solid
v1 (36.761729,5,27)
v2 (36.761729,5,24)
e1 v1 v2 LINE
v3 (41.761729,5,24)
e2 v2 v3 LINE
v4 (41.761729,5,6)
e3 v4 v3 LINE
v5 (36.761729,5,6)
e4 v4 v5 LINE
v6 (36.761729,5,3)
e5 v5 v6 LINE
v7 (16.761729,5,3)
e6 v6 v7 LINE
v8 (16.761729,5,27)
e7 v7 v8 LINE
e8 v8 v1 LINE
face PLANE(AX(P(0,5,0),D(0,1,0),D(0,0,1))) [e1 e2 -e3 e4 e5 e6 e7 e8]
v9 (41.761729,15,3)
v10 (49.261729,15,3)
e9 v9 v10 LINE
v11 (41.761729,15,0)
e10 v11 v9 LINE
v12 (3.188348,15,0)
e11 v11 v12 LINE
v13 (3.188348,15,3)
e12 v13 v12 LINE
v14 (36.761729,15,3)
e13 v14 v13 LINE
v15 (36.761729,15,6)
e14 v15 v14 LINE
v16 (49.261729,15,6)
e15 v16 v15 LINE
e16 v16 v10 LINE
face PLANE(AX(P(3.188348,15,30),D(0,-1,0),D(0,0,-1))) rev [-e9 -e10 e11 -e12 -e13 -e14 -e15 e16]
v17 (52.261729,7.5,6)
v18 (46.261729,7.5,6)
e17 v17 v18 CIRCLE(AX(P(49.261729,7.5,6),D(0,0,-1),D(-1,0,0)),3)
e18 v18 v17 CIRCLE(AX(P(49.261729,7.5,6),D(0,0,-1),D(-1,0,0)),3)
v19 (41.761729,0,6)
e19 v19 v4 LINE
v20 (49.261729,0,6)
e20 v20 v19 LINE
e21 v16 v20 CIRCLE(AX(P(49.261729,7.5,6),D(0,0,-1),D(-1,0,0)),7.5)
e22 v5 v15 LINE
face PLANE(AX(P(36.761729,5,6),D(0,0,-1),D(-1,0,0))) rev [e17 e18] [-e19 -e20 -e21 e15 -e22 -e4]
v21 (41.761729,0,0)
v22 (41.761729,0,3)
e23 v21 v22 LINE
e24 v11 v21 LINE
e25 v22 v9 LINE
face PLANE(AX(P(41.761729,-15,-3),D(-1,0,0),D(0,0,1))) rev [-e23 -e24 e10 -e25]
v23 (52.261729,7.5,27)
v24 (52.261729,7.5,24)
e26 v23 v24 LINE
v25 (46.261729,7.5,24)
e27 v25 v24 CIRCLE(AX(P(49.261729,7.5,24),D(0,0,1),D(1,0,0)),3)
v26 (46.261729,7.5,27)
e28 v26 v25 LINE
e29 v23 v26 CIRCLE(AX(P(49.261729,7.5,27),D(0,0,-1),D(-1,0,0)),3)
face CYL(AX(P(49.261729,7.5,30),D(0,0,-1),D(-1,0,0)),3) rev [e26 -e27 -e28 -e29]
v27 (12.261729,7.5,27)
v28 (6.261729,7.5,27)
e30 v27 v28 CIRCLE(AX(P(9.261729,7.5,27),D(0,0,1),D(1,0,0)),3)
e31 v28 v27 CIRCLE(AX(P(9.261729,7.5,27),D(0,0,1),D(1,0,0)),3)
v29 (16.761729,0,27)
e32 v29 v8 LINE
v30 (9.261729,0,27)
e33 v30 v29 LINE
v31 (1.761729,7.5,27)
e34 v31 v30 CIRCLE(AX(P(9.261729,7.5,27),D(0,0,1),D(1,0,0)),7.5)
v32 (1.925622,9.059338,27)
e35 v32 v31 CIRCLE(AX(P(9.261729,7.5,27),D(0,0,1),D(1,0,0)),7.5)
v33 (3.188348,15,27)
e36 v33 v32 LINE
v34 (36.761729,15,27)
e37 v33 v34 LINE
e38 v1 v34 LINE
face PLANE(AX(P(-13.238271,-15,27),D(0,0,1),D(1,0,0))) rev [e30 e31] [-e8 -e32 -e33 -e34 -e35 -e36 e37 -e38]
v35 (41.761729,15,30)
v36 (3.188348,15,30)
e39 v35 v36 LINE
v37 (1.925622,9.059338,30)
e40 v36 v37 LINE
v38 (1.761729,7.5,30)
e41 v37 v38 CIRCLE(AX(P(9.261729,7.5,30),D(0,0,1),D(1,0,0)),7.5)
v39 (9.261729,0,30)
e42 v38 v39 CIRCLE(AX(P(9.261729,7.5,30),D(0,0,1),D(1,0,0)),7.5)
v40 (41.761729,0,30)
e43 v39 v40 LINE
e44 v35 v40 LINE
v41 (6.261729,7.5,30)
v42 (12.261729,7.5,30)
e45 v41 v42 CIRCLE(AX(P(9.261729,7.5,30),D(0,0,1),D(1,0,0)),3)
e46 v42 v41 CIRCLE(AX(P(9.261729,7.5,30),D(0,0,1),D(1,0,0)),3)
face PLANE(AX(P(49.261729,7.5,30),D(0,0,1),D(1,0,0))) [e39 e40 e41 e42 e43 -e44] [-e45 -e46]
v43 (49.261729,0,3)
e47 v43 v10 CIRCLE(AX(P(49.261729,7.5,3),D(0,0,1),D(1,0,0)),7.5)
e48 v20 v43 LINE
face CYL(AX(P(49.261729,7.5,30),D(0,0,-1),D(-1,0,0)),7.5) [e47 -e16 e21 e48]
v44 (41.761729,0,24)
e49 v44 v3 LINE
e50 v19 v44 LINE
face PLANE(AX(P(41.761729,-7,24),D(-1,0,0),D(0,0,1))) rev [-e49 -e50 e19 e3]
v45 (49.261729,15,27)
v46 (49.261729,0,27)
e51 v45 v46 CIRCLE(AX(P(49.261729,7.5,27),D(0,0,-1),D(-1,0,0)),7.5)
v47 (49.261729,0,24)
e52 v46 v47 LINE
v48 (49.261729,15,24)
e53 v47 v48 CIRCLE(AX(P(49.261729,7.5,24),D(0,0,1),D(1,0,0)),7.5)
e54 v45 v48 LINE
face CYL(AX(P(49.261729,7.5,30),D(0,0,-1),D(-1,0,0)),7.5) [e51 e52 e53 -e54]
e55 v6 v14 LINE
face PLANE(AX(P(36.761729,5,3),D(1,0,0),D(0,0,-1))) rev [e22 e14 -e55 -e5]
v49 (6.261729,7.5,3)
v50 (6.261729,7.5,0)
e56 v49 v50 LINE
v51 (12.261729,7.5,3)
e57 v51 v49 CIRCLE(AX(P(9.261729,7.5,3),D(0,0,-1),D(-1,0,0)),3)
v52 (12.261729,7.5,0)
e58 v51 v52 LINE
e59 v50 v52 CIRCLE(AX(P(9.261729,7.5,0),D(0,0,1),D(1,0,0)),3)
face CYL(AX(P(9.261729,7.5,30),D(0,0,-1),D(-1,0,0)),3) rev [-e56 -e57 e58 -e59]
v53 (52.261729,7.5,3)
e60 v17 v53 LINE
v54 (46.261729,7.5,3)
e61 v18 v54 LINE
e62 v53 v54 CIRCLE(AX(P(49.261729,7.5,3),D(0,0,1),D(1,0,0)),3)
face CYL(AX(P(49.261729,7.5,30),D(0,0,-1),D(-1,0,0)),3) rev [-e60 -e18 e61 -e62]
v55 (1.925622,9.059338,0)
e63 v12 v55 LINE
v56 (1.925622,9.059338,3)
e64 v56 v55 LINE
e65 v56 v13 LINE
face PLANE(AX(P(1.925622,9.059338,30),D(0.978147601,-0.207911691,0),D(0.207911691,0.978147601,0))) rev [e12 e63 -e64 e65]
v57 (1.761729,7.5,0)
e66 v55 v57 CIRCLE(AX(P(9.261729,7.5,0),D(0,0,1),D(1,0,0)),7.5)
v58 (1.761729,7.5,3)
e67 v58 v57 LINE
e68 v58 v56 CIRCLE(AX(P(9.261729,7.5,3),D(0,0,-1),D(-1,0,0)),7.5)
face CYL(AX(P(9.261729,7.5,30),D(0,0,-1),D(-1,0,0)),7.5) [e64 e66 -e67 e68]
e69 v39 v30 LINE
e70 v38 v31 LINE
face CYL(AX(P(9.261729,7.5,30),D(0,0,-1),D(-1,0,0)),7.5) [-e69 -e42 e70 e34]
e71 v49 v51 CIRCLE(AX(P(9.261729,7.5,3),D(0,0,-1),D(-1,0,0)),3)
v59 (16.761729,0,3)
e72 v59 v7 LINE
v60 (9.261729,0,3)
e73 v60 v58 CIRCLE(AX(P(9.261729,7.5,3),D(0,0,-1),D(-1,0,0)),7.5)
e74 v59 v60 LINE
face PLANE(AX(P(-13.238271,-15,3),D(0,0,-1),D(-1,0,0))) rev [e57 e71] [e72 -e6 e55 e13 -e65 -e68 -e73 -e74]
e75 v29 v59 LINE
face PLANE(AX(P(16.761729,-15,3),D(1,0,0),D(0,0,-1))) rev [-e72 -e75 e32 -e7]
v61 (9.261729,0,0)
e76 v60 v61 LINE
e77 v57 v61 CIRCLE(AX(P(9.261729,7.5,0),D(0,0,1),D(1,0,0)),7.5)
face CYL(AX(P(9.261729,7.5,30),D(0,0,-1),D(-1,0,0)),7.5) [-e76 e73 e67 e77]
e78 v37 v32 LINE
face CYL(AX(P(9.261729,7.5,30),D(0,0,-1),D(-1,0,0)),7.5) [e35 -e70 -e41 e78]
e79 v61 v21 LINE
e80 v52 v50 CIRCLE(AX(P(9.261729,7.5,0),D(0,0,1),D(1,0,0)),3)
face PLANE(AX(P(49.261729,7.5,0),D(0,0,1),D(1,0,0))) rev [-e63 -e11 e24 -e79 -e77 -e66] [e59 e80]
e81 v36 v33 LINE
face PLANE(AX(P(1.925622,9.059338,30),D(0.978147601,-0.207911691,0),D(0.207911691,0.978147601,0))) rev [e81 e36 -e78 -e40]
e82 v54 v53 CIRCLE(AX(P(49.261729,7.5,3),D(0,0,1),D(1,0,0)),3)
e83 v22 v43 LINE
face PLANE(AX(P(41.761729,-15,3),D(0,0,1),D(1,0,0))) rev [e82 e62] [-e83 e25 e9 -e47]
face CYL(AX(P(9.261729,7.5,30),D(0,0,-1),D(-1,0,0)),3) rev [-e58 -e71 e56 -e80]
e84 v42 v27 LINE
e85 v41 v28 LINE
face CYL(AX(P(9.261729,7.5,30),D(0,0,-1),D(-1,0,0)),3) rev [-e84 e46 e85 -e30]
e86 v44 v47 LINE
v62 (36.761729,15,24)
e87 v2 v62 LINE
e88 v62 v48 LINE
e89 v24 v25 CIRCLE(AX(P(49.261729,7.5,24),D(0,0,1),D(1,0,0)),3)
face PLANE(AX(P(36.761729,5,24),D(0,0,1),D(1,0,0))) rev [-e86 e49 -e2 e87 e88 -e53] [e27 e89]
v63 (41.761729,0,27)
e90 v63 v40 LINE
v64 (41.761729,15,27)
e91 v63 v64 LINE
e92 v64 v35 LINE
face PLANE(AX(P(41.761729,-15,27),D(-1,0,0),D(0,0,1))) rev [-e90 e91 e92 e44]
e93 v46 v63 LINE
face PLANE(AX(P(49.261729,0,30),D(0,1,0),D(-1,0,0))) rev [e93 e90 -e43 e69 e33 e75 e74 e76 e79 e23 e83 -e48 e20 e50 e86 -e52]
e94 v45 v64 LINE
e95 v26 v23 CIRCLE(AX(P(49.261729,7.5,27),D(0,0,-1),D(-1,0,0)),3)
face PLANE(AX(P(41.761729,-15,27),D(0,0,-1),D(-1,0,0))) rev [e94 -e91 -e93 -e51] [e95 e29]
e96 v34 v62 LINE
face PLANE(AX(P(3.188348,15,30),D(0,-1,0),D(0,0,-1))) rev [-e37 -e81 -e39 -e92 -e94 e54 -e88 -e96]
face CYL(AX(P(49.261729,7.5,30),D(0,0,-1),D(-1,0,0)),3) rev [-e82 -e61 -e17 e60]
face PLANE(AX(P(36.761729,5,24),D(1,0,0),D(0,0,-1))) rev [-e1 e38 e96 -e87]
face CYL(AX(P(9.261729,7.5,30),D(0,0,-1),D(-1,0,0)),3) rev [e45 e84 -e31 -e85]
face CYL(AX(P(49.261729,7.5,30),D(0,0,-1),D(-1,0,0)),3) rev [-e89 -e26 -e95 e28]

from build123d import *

# Parameters (mm, degrees)
SKETCH1_R           = 3
BOSS_EXTRUDE1_DEPTH = 30
SKETCH2_W           = 30
SKETCH2_H           = 24
SKETCH2_H_2         = 6
CUT_EXTRUDE1_DEPTH  = 30
CUT_EXTRUDE2_DEPTH  = 10
SKETCH4_W           = 29.142135624
SKETCH4_H           = 18
CUT_EXTRUDE3_DEPTH  = 12


with BuildPart() as part:
    # Sketch1 → Boss-Extrude1 (new body)
    with BuildSketch(Plane.XY):
        with BuildLine():
            Line((1.925621669, 9.059337681), (3.188348425, 15))
            Line((3.188348425, 15), (49.261728674, 15))
            ThreePointArc((49.261728674, 15), (56.761728674, 7.5), (49.261728674, 0))
            Line((49.261728674, 0), (9.261728674, 0))
            ThreePointArc((9.261728674, 0), (3.433133963, 2.780097067), (1.925621669, 9.059337681))
        make_face()
        with Locations((9.261728674, 7.5)):
            Circle(SKETCH1_R, mode=Mode.SUBTRACT)
        with Locations((49.261728674, 7.5)):
            Circle(SKETCH1_R, mode=Mode.SUBTRACT)
    extrude(amount=BOSS_EXTRUDE1_DEPTH)

    # Sketch2 → Cut-Extrude1 (cut)
    with BuildSketch(Plane(origin=(0, 15, 0), x_dir=(1, 0, 0), z_dir=(0, 1, 0))):
        with Locations((1.761728674, -15)):
            Rectangle(SKETCH2_W, SKETCH2_H)
        with Locations((56.761728674, 0)):
            Rectangle(SKETCH2_W, SKETCH2_H_2)
        with Locations((56.761728674, -30)):
            Rectangle(SKETCH2_W, SKETCH2_H_2)
    extrude(amount=-CUT_EXTRUDE1_DEPTH, mode=Mode.SUBTRACT)

    # Sketch3 → Cut-Extrude2 (cut)
    with BuildSketch(Plane(origin=(0, 15, 0), x_dir=(1, 0, 0), z_dir=(0, 1, 0))):
        Polygon((-3.238271326, -3), (36.761728674, -3), (36.761728674, -6), (65.37522755, -6), (65.37522755, -24), (36.761728674, -24), (36.761728674, -27), (-3.238271326, -27), align=None)
    extrude(amount=-CUT_EXTRUDE2_DEPTH, mode=Mode.SUBTRACT)

    # Sketch4 → Cut-Extrude3 (cut)
    with BuildSketch(Plane(origin=(0, 5, 0), x_dir=(1, 0, 0), z_dir=(0, 1, 0))):
        with Locations((56.332796486, -15)):
            Rectangle(SKETCH4_W, SKETCH4_H)
    extrude(amount=-CUT_EXTRUDE3_DEPTH, mode=Mode.SUBTRACT)


solid = part.part
